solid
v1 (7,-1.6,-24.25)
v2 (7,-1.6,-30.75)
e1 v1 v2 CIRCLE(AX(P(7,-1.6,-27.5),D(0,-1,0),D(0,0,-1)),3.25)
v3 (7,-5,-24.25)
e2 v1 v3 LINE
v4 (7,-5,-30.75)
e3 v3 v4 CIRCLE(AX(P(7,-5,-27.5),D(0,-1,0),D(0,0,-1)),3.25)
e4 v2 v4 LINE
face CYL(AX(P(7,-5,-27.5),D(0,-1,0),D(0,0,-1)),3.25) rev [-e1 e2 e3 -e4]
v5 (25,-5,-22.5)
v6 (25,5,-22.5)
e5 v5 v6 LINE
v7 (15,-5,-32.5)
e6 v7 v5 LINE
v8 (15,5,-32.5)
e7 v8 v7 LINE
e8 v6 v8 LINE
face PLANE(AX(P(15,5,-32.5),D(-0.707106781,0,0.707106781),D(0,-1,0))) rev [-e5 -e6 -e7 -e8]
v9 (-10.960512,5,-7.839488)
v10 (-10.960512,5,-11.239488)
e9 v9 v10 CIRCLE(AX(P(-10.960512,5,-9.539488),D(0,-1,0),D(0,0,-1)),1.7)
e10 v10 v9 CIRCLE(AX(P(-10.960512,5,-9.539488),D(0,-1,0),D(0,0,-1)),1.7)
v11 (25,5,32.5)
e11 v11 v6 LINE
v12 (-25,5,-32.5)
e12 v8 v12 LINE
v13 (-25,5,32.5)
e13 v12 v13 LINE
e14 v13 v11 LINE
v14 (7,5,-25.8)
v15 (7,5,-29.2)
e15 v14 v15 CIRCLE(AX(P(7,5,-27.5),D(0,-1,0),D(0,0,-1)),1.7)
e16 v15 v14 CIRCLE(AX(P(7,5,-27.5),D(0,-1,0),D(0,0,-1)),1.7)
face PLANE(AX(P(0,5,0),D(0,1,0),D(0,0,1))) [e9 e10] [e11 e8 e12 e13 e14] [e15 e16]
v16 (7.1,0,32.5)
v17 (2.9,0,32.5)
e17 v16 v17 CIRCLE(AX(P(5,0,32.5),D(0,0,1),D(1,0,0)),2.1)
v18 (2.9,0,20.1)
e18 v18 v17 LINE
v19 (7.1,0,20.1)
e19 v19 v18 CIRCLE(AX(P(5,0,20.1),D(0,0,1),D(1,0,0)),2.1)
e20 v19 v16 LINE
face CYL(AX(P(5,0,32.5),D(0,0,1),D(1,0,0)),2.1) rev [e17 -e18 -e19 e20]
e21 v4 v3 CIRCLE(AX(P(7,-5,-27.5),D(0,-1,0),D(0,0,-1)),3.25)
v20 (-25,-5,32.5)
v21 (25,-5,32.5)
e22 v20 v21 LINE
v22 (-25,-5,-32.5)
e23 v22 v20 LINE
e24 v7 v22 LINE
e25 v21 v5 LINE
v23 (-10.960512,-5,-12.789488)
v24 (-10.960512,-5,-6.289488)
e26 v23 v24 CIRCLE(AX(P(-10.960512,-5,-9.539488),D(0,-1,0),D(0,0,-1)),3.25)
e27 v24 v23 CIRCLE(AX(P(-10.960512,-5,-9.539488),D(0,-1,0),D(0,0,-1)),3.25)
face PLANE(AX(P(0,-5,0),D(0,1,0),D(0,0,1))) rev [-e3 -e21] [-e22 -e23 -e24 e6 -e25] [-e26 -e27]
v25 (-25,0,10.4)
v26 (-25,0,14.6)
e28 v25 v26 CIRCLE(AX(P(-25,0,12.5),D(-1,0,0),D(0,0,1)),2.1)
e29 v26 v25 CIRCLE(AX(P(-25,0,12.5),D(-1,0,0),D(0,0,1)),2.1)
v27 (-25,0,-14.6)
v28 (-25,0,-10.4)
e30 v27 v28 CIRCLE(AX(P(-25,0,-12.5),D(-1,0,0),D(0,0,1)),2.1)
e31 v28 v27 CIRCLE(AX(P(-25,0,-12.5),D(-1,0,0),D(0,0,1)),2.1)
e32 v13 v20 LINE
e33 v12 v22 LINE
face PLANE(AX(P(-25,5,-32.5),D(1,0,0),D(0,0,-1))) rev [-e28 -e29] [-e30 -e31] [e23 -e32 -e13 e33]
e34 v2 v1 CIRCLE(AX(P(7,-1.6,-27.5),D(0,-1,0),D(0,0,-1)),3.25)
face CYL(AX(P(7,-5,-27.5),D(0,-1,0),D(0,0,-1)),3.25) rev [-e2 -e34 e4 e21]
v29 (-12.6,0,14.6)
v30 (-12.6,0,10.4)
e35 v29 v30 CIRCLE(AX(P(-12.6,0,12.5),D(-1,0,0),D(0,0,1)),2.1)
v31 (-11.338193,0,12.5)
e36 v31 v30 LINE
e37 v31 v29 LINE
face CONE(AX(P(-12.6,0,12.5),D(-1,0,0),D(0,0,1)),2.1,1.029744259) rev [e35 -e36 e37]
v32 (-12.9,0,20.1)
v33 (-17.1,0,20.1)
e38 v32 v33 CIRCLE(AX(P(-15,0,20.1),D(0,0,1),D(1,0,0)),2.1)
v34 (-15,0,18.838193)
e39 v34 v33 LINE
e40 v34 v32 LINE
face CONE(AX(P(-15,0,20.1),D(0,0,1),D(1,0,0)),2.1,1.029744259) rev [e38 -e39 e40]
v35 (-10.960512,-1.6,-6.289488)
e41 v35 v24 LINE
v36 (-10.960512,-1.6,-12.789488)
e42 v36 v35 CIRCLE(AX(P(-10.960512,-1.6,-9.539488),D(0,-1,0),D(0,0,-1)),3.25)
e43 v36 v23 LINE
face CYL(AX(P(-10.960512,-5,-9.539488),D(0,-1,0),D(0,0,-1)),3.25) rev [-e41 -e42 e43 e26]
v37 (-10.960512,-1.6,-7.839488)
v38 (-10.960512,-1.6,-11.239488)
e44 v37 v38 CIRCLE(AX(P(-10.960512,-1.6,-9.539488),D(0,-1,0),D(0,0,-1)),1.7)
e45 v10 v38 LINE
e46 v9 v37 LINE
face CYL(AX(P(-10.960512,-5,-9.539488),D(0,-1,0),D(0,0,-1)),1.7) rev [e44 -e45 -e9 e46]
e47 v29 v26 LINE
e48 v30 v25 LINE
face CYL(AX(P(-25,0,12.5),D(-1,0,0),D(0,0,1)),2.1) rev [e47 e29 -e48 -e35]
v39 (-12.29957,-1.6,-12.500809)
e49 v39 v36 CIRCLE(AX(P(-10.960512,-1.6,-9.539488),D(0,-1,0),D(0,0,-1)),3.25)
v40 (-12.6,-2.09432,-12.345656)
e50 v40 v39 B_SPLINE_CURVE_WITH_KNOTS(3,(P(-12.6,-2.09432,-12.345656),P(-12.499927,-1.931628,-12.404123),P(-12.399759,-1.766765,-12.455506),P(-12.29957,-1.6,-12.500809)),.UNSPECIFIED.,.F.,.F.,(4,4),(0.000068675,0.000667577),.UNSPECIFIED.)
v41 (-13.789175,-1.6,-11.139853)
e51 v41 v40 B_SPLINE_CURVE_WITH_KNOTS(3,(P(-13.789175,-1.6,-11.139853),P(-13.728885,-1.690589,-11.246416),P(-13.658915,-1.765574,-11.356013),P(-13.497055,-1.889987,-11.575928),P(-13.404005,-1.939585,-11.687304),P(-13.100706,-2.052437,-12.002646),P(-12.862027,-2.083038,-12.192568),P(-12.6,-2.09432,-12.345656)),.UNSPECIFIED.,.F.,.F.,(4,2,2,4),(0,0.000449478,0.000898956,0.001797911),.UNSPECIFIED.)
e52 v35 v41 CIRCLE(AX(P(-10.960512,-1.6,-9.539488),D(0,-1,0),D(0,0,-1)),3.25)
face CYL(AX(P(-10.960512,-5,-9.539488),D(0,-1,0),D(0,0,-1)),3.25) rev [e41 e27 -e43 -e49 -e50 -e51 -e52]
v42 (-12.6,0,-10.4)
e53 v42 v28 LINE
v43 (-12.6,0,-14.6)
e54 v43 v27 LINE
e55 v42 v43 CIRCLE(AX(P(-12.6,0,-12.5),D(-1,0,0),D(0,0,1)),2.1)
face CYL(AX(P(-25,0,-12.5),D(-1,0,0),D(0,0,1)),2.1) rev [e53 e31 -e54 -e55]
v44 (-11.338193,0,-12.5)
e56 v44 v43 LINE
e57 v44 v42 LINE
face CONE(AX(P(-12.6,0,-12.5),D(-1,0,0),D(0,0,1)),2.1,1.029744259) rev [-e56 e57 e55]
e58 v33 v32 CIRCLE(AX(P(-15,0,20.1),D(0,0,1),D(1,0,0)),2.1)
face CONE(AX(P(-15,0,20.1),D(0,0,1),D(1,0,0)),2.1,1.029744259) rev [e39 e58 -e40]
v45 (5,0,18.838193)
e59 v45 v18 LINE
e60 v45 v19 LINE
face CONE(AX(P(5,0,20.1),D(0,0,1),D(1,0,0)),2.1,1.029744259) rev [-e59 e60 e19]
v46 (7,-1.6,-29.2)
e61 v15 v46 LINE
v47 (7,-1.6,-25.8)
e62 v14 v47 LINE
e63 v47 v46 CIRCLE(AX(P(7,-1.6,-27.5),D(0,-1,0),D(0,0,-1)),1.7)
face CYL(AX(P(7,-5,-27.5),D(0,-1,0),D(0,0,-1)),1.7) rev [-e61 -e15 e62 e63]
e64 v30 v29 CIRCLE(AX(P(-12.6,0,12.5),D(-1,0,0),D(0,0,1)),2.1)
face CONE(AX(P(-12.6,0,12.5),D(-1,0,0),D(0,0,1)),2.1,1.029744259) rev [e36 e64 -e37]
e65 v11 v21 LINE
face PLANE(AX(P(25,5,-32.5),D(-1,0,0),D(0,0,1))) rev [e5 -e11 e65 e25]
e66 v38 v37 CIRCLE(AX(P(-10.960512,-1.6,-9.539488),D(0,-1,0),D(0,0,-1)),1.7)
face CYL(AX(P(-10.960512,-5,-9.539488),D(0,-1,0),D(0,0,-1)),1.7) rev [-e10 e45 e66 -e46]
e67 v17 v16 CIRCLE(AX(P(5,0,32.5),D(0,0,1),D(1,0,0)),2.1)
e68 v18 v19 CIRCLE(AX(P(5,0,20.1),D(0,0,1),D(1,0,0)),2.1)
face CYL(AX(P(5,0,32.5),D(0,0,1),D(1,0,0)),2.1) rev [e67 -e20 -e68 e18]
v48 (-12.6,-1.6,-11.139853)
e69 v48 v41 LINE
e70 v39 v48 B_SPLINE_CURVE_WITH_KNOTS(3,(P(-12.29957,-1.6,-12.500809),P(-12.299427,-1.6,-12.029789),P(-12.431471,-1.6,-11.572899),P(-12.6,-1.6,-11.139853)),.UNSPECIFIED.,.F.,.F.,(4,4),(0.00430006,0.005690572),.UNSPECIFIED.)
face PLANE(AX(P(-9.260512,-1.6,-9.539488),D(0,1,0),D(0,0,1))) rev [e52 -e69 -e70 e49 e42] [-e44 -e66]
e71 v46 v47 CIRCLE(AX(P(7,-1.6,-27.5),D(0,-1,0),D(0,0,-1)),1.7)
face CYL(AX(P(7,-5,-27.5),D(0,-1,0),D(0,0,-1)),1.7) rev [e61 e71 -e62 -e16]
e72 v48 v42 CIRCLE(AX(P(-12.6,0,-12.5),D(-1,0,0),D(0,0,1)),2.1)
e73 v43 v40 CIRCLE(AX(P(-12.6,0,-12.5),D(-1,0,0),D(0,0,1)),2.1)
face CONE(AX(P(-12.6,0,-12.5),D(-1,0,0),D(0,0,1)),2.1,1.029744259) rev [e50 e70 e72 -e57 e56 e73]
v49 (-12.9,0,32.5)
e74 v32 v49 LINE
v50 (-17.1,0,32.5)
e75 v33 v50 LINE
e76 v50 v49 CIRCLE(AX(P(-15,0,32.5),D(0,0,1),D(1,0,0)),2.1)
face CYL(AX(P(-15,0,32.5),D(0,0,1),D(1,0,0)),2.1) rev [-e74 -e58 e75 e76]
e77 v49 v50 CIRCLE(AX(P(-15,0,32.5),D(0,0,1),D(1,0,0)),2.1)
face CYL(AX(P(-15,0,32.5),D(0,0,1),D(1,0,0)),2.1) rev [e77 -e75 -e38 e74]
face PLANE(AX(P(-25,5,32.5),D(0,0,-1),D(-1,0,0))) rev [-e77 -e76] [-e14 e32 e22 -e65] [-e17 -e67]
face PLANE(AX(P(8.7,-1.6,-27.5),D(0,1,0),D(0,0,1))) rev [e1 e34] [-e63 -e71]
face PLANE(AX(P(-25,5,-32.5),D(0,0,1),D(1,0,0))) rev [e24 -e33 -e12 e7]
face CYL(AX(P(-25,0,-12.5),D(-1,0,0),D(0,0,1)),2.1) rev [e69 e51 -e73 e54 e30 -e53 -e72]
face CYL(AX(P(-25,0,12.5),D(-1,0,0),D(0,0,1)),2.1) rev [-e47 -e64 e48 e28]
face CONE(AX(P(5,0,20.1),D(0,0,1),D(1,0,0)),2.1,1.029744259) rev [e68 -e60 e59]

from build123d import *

# Parameters (mm, degrees)
SKETCH_1_W                   = 50
SKETCH_1_H                   = 65
EXTRUDE_1_DEPTH              = 5
CHAMFER_1_SIZE               = 10
HOLE_WIZARD_M5_1_D           = 4.2
HOLE_WIZARD_M5_1_DEPTH       = 12.4
HOLE_WIZARD_M5_1_TIP         = 1.2618073
HOLE_WIZARD_M3_1_D           = 3.4
HOLE_WIZARD_M3_1_CBORE_D     = 6.5
HOLE_WIZARD_M3_1_CBORE_DEPTH = 3.4
HOLE_WIZARD_M5_2_D           = 4.2
HOLE_WIZARD_M5_2_DEPTH       = 12.4
HOLE_WIZARD_M5_2_TIP         = 1.2618073


with BuildPart() as part:
    # 草图1 → 凸台-拉伸1 (new, symmetric)
    with BuildSketch(Plane(origin=(0, 0, 0), x_dir=(1, 0, 0), z_dir=(0, 1, 0))):
        Rectangle(SKETCH_1_W, SKETCH_1_H)
    extrude(amount=EXTRUDE_1_DEPTH, both=True)

    # 倒角1
    chamfer_1_edges = [part.edges().sort_by_distance(p)[0] for p in [
        (25, 0, -32.5),
    ]]
    chamfer(chamfer_1_edges, length=CHAMFER_1_SIZE)

    # M5 螺纹孔1
    with Locations(Plane.ZY.offset(25)):
        with Locations((-12.5, 0), (12.5, 0)):
            Hole(HOLE_WIZARD_M5_1_D / 2, depth=HOLE_WIZARD_M5_1_DEPTH)
            with Locations((0, 0, -(HOLE_WIZARD_M5_1_DEPTH + HOLE_WIZARD_M5_1_TIP / 2))):  # 118° drill point
                Cone(0, HOLE_WIZARD_M5_1_D / 2, HOLE_WIZARD_M5_1_TIP, mode=Mode.SUBTRACT)

    # M3 六角凹头螺钉的柱形沉头孔1 (through all)
    with Locations(Plane(origin=(0, -5, 0), x_dir=(-1, 0, 0), z_dir=(0, -1, 0))):
        with Locations((-7, 27.5), (10.960512242, 9.539487758)):
            CounterBoreHole(HOLE_WIZARD_M3_1_D / 2, HOLE_WIZARD_M3_1_CBORE_D / 2, HOLE_WIZARD_M3_1_CBORE_DEPTH)

    # M5 螺纹孔2
    with Locations(Plane.XY.offset(32.5)):
        with Locations((-15, 0), (5, 0)):
            Hole(HOLE_WIZARD_M5_2_D / 2, depth=HOLE_WIZARD_M5_2_DEPTH)
            with Locations((0, 0, -(HOLE_WIZARD_M5_2_DEPTH + HOLE_WIZARD_M5_2_TIP / 2))):  # 118° drill point
                Cone(0, HOLE_WIZARD_M5_2_D / 2, HOLE_WIZARD_M5_2_TIP, mode=Mode.SUBTRACT)


solid = part.part
